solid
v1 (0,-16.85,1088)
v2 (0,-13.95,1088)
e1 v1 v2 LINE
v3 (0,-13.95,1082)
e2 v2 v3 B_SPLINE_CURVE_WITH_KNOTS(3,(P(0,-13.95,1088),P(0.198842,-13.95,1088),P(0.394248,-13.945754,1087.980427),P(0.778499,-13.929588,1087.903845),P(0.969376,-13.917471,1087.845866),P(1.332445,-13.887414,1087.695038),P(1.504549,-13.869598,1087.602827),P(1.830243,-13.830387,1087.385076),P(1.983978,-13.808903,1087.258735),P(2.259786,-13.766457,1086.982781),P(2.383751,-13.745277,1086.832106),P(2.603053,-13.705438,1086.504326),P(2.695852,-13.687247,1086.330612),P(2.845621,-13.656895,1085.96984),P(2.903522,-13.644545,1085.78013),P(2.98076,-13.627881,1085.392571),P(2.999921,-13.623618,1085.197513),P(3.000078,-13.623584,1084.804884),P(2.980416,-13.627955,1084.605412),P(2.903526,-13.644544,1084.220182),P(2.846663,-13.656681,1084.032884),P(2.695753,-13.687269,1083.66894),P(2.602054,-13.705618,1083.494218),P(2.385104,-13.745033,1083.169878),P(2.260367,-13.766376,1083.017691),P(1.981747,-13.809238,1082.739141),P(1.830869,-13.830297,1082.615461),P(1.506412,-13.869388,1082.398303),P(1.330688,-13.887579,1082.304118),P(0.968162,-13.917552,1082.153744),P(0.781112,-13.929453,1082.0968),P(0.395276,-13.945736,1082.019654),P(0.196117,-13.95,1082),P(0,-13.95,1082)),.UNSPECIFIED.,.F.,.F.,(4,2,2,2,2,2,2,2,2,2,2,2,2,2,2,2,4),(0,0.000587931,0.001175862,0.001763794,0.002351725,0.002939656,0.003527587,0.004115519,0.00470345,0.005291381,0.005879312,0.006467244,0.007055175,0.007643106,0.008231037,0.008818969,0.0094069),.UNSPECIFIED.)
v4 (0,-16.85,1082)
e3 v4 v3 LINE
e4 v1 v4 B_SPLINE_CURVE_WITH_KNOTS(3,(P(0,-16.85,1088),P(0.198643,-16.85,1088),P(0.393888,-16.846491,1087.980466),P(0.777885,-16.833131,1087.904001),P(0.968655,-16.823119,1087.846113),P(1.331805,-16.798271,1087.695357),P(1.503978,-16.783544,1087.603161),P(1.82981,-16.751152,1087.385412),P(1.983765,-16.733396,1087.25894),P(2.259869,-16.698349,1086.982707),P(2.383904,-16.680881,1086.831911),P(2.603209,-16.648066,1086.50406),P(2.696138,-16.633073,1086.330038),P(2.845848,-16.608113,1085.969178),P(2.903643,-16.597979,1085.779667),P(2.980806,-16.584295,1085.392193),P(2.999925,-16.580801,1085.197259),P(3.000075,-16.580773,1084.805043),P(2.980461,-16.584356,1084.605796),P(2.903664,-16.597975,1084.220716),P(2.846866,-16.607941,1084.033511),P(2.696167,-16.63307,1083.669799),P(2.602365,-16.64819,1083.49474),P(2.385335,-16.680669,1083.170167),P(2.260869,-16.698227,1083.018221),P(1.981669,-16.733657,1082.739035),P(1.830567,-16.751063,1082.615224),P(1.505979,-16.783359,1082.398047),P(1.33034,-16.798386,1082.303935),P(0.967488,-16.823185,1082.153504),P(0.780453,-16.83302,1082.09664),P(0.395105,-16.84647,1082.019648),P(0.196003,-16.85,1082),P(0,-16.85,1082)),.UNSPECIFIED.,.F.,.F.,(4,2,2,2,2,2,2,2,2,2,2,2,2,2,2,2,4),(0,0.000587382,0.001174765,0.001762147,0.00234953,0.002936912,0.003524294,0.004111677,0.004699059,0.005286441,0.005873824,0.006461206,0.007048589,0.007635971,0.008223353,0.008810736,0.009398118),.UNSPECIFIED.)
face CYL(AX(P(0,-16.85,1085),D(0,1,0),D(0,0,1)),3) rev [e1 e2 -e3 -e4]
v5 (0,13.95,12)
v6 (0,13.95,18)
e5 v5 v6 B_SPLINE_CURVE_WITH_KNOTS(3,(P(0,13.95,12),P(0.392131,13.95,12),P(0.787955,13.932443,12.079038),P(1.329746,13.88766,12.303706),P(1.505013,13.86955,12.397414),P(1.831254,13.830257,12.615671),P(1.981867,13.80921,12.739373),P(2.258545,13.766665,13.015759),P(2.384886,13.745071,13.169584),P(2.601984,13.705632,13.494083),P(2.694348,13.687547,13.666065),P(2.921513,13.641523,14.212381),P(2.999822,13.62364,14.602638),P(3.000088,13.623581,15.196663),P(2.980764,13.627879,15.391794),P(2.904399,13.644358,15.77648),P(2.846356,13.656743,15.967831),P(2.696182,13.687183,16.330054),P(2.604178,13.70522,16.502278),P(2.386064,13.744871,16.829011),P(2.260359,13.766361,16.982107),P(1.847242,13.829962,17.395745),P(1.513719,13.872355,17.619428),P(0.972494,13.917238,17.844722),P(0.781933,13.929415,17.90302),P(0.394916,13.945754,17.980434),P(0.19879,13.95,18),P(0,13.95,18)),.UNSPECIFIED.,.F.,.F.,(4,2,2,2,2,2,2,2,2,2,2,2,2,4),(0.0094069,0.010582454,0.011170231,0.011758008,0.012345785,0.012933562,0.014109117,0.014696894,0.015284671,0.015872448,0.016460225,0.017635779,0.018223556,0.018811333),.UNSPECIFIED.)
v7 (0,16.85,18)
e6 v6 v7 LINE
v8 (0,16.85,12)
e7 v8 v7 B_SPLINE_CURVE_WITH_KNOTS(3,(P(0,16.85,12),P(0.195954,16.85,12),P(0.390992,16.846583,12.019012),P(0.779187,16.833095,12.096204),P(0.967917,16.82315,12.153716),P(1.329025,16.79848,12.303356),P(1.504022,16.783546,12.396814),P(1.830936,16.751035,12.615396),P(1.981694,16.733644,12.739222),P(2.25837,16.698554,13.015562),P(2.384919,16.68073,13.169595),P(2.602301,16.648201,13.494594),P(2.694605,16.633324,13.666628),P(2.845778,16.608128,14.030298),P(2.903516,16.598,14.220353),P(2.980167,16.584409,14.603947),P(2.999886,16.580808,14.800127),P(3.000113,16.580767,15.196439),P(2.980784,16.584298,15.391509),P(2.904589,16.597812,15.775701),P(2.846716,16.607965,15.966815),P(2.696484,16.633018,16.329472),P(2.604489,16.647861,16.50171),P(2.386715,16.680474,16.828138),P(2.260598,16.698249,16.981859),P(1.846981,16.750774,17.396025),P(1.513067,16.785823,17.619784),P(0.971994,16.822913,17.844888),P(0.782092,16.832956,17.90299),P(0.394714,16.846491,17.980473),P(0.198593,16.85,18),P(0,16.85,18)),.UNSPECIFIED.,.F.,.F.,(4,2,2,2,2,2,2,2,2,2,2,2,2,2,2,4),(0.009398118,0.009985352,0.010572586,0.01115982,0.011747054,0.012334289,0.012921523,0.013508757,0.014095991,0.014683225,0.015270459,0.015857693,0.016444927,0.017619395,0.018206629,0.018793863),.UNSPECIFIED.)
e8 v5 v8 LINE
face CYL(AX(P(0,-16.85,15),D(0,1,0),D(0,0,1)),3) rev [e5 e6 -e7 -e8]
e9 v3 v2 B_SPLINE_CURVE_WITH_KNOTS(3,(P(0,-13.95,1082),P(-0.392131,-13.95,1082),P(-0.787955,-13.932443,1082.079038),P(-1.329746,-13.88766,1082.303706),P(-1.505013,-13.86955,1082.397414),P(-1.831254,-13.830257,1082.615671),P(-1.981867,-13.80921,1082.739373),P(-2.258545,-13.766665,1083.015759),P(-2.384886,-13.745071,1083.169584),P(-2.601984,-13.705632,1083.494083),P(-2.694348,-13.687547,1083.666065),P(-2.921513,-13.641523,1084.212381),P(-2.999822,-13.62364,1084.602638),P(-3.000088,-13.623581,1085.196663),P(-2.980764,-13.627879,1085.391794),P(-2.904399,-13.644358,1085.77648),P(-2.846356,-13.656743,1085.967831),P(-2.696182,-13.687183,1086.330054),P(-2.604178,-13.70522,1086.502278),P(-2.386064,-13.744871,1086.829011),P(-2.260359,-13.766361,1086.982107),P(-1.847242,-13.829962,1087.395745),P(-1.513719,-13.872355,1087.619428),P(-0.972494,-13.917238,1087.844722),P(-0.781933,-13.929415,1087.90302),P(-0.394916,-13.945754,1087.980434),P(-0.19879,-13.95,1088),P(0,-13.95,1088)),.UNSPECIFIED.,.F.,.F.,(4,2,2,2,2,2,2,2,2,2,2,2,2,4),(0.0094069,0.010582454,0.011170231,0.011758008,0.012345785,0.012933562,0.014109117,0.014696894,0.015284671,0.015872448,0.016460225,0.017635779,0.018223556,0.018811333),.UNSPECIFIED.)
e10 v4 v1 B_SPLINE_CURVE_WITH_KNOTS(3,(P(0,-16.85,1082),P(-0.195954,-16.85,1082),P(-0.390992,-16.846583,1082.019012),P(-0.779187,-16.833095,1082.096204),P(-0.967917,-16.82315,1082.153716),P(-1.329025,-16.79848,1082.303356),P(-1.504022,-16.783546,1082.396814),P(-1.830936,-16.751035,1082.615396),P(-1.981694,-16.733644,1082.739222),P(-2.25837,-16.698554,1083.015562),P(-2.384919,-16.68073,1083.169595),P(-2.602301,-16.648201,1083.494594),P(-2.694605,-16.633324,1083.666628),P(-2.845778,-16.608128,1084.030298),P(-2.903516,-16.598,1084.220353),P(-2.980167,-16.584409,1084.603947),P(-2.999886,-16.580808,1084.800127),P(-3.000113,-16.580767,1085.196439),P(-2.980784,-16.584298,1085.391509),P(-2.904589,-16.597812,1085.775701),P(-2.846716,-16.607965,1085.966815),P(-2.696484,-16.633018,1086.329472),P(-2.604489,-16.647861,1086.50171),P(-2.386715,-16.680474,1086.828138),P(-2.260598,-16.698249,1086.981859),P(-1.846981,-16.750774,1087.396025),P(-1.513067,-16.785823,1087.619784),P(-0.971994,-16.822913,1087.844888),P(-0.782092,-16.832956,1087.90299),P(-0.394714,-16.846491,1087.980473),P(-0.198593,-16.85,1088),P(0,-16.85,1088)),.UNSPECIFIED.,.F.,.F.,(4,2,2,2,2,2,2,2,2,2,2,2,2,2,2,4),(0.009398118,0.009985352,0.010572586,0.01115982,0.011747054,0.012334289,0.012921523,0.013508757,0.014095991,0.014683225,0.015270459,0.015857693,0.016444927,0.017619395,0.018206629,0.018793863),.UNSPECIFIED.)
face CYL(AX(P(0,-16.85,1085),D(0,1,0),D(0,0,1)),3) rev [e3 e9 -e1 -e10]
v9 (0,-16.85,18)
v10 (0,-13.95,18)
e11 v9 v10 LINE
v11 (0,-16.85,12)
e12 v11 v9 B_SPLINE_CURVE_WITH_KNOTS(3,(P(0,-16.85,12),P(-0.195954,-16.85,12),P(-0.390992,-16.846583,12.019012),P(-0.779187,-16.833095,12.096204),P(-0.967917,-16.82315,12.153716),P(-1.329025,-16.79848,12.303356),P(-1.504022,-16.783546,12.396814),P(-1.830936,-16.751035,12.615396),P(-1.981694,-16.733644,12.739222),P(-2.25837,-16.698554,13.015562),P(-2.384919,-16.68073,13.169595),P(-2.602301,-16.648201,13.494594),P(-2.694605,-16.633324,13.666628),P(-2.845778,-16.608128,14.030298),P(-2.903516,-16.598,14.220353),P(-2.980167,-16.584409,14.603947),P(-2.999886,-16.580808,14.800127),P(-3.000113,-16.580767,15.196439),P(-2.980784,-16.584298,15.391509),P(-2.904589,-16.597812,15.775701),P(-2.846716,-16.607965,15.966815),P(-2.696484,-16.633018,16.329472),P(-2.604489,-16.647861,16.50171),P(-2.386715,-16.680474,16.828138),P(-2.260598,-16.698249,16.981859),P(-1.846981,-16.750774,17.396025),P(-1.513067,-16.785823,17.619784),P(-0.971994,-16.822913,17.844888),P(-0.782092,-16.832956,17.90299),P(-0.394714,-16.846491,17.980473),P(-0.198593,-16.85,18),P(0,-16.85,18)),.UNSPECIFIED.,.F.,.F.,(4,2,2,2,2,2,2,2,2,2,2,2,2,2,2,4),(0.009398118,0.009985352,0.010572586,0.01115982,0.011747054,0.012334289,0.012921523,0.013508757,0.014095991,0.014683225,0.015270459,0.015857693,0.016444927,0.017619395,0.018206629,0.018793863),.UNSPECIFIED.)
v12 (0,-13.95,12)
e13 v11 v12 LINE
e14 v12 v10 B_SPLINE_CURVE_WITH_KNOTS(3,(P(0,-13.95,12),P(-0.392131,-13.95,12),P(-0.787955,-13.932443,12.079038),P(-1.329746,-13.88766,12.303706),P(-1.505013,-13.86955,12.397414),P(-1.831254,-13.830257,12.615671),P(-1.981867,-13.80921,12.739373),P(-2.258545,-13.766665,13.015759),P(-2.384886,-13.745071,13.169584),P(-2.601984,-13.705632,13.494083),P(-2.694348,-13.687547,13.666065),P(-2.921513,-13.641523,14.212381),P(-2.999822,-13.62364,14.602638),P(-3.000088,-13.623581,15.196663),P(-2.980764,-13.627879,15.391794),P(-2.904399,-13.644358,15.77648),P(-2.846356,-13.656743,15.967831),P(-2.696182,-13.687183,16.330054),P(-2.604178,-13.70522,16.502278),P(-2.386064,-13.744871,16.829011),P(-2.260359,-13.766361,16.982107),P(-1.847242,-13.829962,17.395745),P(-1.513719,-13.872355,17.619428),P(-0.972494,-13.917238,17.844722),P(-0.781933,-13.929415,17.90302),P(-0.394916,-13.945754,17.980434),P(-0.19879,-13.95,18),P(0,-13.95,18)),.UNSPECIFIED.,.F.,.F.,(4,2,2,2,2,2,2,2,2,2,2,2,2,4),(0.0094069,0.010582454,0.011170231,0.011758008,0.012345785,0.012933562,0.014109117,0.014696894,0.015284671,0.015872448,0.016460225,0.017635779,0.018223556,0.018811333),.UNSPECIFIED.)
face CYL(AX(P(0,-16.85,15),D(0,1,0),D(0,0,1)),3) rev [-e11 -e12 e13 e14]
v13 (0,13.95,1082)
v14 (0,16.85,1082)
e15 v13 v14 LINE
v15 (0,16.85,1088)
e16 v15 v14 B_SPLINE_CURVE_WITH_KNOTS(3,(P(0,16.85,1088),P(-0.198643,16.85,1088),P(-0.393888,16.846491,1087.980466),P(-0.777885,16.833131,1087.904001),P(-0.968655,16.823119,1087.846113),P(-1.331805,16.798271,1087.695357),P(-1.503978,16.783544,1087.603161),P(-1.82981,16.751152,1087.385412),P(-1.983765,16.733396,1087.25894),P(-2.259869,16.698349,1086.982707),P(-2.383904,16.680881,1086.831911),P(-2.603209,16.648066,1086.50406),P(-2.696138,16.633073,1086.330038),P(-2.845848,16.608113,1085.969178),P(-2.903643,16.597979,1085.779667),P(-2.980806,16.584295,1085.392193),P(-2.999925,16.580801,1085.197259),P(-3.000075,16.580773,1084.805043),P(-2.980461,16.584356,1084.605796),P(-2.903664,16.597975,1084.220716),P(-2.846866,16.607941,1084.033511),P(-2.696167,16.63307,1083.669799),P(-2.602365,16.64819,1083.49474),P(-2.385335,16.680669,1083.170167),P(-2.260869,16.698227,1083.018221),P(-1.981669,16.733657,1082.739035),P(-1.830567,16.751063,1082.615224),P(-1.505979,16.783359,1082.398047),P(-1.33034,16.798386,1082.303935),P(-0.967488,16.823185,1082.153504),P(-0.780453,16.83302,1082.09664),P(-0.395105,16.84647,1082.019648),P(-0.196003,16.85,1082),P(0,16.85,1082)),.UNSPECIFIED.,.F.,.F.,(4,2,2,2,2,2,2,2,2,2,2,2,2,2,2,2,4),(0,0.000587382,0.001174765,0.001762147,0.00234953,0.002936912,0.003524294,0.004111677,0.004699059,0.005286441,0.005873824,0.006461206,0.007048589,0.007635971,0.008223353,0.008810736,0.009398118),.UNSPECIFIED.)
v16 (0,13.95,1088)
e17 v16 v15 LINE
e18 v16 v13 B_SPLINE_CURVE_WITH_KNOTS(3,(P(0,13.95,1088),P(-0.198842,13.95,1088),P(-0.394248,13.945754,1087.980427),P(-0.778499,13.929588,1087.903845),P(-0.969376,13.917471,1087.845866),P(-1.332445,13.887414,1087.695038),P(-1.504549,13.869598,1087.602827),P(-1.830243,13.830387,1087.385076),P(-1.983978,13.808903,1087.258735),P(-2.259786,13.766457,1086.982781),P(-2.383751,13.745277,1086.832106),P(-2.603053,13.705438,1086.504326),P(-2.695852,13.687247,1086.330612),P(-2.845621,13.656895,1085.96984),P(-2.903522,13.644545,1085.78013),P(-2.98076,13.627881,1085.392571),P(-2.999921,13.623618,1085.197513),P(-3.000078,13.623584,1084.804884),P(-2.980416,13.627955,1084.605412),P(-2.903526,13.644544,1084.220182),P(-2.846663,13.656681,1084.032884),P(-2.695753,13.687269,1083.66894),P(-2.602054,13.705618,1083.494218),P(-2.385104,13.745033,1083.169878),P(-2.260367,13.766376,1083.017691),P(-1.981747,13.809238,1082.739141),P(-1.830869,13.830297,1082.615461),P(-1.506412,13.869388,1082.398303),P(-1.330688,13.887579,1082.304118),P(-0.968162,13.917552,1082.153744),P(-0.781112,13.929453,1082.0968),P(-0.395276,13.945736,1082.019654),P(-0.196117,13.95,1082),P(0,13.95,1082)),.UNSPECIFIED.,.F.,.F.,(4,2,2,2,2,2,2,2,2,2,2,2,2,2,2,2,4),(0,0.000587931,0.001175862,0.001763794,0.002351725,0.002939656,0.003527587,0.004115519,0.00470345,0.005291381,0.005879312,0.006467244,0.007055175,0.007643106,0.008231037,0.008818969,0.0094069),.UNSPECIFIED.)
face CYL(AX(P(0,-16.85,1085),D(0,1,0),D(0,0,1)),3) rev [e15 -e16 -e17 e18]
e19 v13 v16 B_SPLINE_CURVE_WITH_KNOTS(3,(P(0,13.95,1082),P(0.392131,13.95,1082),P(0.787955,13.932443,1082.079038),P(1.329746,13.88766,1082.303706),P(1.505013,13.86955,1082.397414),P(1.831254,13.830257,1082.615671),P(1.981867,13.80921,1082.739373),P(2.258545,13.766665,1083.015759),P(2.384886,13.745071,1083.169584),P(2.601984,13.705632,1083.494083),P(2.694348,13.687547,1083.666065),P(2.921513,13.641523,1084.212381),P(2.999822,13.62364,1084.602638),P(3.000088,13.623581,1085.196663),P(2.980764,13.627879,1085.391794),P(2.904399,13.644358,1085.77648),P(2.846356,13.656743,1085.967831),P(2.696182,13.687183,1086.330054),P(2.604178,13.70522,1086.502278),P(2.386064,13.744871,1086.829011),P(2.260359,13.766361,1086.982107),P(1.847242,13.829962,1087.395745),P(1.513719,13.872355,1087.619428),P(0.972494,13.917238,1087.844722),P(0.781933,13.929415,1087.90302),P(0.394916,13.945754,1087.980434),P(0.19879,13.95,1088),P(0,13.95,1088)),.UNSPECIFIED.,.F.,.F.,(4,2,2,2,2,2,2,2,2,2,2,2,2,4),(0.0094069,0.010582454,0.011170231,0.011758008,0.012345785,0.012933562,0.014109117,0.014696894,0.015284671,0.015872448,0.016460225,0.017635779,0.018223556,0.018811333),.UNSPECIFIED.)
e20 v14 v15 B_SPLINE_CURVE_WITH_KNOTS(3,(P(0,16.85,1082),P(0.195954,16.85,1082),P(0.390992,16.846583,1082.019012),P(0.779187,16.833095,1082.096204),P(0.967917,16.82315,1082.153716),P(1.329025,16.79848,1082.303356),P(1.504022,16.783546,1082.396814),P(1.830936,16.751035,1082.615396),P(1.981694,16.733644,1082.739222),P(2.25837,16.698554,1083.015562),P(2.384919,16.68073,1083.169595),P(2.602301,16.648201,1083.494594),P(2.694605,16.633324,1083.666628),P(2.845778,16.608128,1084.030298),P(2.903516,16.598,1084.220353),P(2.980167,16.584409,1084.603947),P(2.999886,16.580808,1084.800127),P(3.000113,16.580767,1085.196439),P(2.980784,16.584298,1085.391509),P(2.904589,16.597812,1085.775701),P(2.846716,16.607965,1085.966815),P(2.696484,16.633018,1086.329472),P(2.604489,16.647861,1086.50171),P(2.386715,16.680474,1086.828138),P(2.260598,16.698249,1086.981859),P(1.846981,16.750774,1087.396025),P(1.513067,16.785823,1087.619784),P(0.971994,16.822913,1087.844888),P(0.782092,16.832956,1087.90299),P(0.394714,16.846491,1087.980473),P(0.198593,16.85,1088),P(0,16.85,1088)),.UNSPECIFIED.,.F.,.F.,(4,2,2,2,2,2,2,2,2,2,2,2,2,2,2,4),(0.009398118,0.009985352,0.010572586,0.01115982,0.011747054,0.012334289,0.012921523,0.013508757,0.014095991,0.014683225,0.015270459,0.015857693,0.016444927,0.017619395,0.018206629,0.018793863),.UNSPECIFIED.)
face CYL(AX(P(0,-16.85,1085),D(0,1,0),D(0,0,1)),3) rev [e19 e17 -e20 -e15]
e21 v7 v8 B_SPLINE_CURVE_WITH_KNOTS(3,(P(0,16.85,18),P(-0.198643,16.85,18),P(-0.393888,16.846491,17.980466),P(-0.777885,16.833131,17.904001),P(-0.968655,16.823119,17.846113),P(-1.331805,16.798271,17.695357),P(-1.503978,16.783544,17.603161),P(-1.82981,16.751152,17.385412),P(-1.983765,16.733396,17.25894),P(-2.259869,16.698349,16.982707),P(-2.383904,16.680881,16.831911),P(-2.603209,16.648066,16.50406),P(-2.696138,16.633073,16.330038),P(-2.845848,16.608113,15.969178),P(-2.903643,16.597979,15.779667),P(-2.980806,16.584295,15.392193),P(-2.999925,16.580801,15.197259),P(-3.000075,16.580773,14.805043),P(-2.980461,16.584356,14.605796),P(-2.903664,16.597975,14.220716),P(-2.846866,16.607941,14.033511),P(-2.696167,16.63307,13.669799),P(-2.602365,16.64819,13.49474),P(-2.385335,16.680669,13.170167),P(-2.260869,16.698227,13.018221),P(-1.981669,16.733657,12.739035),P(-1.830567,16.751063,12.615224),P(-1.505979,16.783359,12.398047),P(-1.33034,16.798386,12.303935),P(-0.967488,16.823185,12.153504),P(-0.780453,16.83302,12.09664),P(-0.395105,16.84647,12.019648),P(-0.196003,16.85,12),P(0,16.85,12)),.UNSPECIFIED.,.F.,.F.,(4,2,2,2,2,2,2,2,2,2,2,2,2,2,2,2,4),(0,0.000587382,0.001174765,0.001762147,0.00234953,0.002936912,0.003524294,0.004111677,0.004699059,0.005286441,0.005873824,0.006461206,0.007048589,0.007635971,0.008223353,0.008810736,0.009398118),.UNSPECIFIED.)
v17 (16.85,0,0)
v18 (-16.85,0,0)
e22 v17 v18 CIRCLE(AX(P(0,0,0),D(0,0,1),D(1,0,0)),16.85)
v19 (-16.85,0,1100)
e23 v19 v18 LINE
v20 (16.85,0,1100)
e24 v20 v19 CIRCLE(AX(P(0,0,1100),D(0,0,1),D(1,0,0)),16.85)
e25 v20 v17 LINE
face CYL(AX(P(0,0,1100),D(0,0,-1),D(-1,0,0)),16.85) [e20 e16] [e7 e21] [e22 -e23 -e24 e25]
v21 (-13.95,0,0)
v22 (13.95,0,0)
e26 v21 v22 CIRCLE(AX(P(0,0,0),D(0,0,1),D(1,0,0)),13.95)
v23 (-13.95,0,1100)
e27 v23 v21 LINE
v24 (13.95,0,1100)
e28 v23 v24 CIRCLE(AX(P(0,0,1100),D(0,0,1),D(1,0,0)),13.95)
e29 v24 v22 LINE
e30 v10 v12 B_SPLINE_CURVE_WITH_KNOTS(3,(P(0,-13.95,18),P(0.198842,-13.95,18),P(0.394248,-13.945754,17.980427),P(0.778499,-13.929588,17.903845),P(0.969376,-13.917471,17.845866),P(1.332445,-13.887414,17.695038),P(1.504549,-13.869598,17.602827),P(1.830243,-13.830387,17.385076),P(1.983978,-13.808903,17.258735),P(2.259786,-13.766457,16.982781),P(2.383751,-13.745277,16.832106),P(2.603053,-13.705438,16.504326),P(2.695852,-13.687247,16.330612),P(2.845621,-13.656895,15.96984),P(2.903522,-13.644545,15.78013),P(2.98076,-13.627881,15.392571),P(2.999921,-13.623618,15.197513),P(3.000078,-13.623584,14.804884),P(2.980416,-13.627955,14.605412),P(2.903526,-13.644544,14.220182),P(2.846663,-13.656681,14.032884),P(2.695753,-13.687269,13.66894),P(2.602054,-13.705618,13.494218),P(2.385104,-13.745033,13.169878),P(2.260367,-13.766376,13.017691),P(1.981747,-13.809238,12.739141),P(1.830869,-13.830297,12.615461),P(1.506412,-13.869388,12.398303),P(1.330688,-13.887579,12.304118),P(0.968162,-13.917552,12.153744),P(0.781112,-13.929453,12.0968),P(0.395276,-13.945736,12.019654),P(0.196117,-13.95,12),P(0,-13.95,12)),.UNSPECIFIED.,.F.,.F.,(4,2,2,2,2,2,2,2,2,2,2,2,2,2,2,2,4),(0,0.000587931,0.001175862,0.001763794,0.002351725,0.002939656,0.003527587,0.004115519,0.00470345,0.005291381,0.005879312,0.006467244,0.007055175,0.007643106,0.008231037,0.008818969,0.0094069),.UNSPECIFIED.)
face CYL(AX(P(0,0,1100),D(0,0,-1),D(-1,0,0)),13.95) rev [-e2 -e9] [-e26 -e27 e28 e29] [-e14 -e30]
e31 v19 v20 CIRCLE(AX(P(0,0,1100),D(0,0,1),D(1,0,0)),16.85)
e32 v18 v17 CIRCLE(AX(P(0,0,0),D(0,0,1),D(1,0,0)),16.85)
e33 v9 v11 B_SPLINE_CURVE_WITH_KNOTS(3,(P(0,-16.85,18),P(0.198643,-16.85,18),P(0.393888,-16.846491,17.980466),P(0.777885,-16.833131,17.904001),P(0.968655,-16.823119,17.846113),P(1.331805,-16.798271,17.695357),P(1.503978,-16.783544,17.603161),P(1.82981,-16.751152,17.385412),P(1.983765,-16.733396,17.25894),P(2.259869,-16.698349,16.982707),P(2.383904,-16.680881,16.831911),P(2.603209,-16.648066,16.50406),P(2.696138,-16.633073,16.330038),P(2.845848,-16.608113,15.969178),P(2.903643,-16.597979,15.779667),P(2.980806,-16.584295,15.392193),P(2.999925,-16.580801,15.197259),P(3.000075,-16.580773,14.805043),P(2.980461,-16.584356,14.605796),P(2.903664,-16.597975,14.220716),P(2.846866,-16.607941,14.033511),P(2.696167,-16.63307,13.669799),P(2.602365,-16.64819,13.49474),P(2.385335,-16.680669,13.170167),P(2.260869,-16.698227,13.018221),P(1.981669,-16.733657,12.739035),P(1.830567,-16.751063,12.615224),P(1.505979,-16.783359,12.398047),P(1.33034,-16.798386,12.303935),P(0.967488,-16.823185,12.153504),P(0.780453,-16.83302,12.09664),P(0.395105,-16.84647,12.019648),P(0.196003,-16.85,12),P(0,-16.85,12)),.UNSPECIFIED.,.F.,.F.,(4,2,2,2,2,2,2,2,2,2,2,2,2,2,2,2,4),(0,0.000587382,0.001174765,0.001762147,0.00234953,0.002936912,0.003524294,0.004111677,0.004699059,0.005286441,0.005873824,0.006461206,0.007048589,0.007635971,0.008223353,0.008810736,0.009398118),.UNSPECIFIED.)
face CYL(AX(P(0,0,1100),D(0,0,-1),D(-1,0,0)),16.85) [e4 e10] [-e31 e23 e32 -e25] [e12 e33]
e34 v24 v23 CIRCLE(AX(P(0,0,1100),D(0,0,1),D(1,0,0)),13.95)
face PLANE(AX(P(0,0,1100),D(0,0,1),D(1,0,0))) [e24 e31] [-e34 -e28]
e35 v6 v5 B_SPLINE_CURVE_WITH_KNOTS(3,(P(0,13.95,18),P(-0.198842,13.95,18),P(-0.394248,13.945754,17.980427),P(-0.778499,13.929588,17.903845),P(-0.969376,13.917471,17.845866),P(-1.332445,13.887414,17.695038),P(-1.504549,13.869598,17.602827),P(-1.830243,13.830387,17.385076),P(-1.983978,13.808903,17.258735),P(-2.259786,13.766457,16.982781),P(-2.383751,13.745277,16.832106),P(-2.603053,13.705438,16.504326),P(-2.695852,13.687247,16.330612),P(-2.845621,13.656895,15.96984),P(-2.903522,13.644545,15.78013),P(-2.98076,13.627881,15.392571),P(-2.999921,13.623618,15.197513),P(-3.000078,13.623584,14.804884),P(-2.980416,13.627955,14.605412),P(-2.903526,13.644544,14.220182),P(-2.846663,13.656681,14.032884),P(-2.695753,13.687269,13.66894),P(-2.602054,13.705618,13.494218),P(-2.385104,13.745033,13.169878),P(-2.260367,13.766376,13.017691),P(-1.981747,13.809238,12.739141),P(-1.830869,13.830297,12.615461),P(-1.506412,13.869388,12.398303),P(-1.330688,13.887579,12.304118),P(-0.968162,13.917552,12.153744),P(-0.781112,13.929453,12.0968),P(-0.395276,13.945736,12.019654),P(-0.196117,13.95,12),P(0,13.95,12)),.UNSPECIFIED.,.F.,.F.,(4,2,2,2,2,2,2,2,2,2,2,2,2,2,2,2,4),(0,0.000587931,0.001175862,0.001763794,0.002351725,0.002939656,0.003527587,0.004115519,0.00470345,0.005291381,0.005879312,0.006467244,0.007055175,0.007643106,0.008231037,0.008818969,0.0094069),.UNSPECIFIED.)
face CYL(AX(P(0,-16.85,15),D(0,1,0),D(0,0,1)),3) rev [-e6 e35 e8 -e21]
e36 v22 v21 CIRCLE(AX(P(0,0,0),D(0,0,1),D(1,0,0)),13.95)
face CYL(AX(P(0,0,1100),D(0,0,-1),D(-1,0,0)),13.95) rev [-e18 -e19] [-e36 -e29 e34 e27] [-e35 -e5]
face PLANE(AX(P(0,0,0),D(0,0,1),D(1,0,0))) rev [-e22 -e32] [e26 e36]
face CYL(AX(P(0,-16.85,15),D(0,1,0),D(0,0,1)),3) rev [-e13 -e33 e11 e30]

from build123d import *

# Parameters (mm, degrees)
SKETCH_1_R          = 16.85
SKETCH_1_R_2        = 13.95
EXTRUDE_1_DEPTH     = 1100
SKETCH_2_R          = 3
CUT_EXTRUDE_1_DEPTH = 16.85


with BuildPart() as part:
    # 草图1 → 凸台-拉伸1 (new body)
    with BuildSketch(Plane.XY):
        Circle(SKETCH_1_R)
        Circle(SKETCH_1_R_2, mode=Mode.SUBTRACT)
    extrude(amount=EXTRUDE_1_DEPTH)

    # 草图2 → 切除-拉伸1 (cut, symmetric)
    with BuildSketch(Plane(origin=(0, 0, 0), x_dir=(1, 0, 0), z_dir=(0, 1, 0))):
        with Locations(Location((0, -15, 0), (0, 0, 270))):
            Circle(SKETCH_2_R)
        with Locations(Location((0, -1085, 0), (0, 0, 270))):
            Circle(SKETCH_2_R)
    extrude(amount=CUT_EXTRUDE_1_DEPTH, both=True, mode=Mode.SUBTRACT)


solid = part.part
